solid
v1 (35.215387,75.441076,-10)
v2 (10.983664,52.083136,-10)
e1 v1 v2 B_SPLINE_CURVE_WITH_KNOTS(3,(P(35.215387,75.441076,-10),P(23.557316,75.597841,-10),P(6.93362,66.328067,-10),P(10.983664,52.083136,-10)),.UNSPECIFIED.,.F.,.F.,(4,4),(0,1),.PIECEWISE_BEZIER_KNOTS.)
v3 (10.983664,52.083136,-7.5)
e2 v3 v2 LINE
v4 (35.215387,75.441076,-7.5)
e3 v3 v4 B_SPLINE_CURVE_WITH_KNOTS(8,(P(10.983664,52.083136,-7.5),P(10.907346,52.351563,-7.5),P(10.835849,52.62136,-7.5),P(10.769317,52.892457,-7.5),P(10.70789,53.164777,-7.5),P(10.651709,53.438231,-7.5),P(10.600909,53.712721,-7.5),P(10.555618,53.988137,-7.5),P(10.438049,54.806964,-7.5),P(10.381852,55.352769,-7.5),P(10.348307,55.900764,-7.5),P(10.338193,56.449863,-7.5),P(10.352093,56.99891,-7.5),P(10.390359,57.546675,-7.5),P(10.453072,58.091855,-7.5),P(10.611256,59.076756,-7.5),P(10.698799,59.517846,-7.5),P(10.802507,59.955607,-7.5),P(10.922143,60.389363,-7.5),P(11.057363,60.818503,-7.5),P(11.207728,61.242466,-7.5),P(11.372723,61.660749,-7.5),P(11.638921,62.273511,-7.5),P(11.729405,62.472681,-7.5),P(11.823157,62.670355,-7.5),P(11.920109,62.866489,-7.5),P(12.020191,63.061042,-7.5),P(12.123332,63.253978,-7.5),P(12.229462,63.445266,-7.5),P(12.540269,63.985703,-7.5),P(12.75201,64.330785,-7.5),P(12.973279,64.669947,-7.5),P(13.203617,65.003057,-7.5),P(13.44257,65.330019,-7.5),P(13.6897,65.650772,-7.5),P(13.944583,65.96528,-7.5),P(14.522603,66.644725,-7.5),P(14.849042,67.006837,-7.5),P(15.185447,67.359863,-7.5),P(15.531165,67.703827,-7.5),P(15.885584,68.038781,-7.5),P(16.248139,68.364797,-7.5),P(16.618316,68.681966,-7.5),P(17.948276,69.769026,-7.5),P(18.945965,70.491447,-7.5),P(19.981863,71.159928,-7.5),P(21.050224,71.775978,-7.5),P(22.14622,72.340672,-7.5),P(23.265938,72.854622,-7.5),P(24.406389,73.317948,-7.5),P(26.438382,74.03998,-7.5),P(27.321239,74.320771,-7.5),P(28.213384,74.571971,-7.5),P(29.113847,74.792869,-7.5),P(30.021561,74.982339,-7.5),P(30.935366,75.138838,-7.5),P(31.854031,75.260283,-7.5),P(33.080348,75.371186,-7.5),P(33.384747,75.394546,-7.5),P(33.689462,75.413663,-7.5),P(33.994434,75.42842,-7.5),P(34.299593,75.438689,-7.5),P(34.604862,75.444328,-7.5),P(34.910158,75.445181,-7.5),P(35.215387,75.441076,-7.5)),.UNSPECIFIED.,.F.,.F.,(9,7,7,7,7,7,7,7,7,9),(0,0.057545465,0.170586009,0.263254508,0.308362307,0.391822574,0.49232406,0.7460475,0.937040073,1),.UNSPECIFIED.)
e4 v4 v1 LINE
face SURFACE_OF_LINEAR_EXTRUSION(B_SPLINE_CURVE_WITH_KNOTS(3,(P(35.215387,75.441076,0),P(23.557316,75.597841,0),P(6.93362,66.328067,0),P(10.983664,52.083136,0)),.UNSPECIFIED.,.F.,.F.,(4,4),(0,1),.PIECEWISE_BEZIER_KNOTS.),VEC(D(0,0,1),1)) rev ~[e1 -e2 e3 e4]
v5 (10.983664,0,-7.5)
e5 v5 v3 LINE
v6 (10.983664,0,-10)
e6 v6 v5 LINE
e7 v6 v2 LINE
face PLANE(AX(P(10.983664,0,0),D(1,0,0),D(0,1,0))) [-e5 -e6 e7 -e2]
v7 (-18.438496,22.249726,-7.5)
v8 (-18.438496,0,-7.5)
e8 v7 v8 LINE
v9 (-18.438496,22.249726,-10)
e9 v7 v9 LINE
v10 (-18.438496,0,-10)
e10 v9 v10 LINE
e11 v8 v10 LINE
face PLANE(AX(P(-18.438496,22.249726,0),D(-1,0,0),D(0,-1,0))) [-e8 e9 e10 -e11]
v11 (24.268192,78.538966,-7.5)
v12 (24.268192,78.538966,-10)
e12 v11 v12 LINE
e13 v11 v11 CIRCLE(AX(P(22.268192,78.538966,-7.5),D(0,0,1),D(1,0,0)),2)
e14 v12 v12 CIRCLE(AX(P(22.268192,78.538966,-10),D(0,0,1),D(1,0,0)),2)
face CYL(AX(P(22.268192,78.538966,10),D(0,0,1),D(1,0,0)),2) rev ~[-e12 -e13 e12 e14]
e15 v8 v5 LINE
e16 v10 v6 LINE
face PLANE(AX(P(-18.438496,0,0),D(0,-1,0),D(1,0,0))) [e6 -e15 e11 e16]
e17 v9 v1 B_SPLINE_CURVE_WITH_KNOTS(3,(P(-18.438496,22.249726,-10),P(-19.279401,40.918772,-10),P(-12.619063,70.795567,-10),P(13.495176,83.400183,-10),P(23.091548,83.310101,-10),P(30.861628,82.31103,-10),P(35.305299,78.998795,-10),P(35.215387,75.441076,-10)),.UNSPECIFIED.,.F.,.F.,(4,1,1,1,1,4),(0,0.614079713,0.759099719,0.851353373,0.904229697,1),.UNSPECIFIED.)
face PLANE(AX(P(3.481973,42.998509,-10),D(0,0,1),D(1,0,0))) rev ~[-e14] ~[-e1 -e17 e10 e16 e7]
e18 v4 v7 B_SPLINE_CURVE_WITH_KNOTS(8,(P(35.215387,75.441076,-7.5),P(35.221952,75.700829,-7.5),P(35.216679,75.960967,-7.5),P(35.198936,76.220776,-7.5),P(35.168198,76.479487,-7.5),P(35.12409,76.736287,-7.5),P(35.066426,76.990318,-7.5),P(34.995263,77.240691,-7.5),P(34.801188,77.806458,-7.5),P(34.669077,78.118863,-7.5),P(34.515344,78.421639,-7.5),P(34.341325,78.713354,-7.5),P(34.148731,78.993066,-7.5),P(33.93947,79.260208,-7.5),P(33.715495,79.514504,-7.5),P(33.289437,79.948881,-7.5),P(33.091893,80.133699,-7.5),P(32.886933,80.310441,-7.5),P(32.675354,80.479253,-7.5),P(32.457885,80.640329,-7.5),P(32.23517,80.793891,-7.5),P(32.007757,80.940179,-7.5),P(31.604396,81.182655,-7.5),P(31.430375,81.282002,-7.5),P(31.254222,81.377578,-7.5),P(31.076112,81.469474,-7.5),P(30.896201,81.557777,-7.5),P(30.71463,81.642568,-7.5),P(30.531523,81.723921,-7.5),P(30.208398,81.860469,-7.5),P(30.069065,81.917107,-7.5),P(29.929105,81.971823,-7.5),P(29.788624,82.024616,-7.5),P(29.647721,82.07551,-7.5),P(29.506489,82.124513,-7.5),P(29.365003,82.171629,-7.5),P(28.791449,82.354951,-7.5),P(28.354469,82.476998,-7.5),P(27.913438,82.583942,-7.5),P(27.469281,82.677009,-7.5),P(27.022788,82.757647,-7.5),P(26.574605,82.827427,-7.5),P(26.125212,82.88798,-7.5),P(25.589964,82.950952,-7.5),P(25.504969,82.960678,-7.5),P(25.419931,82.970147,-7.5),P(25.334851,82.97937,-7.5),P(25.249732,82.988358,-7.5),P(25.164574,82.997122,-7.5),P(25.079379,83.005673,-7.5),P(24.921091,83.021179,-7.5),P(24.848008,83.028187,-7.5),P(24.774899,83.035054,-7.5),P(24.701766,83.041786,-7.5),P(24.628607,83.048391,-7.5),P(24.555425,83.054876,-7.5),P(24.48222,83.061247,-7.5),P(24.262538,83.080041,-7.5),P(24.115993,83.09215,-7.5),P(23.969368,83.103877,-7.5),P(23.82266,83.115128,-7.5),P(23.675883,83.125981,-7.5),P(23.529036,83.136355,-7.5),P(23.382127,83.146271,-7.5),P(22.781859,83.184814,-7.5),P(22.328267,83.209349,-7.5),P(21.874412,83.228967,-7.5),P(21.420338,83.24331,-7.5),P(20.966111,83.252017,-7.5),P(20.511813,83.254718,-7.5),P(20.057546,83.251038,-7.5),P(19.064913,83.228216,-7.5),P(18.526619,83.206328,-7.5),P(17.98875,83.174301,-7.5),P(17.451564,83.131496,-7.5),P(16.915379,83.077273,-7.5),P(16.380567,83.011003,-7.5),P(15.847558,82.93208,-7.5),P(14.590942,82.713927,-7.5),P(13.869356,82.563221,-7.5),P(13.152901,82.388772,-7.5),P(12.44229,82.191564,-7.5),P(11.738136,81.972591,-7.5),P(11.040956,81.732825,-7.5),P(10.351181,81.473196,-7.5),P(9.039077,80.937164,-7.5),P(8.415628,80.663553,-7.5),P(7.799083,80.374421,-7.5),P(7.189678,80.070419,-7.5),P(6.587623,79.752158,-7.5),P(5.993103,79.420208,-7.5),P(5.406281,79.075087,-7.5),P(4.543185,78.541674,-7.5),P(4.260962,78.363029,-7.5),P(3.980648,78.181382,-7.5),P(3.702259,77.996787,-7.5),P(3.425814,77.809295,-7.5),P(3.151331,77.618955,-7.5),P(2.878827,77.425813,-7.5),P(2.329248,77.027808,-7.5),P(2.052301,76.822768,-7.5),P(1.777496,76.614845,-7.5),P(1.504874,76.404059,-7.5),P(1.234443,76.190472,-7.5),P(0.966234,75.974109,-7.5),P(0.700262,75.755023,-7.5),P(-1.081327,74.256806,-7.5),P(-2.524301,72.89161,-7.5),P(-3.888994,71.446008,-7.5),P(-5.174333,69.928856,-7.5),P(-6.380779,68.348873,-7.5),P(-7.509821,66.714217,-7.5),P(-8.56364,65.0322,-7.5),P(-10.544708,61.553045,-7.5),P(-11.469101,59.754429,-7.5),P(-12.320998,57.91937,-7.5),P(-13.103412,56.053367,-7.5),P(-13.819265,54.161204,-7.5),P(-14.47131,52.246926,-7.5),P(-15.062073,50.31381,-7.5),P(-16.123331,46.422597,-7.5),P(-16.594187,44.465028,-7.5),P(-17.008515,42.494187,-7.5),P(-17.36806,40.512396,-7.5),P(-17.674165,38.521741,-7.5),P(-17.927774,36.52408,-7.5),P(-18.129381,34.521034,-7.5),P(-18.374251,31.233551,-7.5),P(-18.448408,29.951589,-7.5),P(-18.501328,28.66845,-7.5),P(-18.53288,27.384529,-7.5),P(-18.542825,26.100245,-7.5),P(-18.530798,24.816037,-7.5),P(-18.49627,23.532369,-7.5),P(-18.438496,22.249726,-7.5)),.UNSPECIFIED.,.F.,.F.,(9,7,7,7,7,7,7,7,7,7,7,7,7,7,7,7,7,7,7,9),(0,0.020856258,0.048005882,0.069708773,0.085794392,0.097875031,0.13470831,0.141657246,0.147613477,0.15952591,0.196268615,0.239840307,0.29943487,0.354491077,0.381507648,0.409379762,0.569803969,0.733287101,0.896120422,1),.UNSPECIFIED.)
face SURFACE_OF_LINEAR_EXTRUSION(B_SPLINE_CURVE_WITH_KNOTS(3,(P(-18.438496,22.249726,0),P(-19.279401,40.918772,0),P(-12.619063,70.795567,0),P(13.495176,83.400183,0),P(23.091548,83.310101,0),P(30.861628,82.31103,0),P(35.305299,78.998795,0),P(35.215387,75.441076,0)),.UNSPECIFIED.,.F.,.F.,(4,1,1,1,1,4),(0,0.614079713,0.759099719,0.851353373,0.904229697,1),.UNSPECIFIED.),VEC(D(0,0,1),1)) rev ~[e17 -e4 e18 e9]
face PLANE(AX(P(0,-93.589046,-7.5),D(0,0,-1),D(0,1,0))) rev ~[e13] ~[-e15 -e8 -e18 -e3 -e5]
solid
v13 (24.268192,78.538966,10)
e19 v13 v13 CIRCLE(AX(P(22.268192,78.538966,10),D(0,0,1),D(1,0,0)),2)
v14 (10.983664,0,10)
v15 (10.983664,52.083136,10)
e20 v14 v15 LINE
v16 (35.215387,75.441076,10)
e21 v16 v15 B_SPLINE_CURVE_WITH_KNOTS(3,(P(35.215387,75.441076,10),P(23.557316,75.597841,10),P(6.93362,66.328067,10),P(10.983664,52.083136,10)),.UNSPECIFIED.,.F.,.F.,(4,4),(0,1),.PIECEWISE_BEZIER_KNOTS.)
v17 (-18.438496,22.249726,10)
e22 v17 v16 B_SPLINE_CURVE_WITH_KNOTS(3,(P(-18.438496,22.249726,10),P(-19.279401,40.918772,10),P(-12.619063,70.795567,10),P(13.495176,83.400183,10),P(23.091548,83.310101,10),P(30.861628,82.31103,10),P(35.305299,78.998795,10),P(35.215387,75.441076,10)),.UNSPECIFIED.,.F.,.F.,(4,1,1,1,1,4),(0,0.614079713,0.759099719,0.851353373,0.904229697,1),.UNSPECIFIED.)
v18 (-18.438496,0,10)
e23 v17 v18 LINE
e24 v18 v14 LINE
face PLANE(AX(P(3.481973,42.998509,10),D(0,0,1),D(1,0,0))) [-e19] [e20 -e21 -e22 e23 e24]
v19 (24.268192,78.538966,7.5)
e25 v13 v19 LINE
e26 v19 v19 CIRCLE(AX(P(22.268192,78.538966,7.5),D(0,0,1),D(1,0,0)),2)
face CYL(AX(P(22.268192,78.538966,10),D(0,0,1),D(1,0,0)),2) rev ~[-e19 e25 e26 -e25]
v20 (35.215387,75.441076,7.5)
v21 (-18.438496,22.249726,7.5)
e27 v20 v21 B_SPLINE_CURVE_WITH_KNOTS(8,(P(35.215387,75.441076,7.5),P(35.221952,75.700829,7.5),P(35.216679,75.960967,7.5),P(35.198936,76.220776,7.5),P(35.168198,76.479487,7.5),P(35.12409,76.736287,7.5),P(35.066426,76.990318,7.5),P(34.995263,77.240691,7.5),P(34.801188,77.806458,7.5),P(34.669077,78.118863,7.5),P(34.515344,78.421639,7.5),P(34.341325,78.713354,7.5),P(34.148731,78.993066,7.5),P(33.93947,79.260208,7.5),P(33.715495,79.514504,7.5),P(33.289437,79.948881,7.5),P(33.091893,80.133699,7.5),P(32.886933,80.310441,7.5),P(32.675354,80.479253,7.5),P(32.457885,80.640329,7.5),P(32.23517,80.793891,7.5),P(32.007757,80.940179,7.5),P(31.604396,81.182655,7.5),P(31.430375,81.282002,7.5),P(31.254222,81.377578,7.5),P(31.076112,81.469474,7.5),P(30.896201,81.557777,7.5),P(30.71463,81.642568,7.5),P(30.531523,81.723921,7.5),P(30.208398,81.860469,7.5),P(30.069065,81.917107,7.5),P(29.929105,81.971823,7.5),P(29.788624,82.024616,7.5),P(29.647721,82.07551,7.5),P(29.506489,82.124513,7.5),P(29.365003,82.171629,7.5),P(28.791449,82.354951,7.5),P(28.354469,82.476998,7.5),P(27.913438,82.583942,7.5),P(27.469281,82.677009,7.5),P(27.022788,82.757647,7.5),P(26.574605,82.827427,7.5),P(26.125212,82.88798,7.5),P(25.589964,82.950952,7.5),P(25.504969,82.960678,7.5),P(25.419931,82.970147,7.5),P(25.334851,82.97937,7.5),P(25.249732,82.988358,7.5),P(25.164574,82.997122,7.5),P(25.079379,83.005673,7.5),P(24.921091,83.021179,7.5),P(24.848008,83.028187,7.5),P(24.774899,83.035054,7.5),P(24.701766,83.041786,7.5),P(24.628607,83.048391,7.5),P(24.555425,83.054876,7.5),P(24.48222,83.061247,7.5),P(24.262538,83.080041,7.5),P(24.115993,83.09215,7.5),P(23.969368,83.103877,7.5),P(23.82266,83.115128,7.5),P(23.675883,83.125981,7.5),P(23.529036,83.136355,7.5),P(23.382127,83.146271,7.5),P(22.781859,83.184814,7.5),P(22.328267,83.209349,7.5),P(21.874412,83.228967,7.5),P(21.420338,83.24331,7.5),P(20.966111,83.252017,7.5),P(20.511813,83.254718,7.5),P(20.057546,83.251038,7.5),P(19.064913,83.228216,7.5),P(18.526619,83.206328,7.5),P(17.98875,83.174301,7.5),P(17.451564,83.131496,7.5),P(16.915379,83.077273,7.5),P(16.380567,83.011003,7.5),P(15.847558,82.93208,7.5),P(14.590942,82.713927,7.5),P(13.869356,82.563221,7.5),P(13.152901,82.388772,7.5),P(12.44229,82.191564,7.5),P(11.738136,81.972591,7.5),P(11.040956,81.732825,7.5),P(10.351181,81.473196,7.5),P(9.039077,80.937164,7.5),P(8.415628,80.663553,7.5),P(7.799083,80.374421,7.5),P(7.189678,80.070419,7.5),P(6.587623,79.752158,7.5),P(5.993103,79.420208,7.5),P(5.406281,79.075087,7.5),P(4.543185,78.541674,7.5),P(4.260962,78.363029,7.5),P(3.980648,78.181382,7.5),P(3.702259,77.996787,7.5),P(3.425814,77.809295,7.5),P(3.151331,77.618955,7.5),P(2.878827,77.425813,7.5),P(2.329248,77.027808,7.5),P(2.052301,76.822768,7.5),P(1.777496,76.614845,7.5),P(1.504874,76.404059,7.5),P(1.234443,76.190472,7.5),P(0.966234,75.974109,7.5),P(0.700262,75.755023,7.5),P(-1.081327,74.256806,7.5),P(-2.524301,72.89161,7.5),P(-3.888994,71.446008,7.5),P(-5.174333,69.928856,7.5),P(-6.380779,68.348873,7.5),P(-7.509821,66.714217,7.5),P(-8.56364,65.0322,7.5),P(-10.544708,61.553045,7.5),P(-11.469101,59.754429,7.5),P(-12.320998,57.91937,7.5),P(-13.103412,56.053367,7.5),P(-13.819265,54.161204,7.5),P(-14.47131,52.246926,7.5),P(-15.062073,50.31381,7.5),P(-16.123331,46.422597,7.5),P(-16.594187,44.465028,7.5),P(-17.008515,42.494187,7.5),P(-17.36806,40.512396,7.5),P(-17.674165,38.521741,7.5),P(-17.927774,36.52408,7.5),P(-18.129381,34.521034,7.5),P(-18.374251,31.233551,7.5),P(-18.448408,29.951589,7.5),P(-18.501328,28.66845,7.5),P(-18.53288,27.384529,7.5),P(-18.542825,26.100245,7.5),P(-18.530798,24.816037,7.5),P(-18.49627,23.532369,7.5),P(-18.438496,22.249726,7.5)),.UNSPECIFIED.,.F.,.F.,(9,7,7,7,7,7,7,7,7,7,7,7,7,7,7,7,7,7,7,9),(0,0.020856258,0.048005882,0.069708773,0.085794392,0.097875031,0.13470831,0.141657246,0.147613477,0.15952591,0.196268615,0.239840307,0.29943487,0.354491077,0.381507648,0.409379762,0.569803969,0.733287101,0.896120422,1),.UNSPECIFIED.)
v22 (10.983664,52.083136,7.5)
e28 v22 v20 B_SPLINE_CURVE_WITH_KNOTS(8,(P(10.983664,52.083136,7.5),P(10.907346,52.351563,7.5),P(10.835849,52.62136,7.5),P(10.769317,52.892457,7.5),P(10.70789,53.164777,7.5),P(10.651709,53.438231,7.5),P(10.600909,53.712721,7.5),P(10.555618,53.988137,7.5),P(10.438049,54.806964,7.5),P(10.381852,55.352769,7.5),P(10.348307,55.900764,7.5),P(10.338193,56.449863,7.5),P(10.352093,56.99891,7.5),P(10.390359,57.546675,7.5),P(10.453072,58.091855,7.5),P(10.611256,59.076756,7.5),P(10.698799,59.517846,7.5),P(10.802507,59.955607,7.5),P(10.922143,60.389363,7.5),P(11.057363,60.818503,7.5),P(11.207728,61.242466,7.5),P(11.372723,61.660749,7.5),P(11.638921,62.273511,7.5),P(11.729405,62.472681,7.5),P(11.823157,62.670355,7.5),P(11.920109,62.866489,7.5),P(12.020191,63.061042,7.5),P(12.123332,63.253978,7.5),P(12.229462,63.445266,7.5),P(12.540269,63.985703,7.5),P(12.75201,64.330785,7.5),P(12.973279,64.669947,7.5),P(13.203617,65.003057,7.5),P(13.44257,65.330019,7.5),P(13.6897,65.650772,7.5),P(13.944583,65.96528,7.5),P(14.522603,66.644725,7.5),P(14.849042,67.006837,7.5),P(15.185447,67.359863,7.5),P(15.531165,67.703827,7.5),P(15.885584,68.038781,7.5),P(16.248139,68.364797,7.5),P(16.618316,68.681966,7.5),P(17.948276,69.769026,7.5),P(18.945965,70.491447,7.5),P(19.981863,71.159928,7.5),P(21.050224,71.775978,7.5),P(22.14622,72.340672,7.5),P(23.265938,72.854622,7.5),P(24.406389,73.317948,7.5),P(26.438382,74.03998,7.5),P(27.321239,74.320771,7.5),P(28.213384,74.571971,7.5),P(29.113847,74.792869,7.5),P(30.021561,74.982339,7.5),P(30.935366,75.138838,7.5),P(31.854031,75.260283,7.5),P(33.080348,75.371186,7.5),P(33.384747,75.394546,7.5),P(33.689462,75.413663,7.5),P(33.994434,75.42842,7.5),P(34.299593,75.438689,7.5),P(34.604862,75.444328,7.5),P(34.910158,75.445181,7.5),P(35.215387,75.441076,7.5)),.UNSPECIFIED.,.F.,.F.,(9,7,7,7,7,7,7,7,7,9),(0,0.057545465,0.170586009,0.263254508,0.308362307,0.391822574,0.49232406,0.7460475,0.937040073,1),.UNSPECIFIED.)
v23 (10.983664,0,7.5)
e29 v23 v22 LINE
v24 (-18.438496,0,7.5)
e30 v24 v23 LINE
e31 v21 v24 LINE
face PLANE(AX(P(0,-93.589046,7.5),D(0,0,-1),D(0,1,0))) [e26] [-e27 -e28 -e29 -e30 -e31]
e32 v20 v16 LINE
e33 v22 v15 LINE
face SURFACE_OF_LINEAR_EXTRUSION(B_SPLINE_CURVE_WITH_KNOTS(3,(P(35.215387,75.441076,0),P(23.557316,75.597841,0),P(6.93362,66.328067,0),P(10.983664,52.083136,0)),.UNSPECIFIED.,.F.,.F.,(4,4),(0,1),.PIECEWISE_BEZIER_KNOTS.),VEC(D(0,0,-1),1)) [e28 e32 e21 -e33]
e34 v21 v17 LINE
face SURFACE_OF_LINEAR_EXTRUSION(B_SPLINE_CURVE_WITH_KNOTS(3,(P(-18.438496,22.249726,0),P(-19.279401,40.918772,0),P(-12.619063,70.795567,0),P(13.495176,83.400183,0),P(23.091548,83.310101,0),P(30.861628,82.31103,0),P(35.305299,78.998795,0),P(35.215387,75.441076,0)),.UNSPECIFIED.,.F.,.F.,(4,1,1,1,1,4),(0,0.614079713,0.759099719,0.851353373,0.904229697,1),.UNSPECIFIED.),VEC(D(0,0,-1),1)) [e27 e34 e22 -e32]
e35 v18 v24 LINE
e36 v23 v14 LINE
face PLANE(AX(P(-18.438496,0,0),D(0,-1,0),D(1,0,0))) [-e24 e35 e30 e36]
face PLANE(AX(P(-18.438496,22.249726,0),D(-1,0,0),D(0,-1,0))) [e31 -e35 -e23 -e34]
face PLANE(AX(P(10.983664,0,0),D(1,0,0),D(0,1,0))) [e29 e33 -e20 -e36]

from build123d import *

# Parameters (mm, degrees)
EXTRUDE_1_DEPTH     = 10
SKETCH_5_W          = 15
SKETCH_5_H          = 187.17809157
CUT_EXTRUDE_1_DEPTH = 50
SKETCH_6_R          = 2
CUT_EXTRUDE_2_DEPTH = 100


with BuildPart() as part:
    # 草图4 → 凸台-拉伸1 (new, symmetric)
    with BuildSketch(Plane.XY):
        with BuildLine():
            Line((-18.438496173, 0), (10.983664043, 0))
            Line((10.983664043, 0), (10.983664043, 52.083135501))
            add(Edge.make_bspline(
                [(35.215387482, 75.44107623), (23.557315805, 75.597841168), (6.9336204, 66.328066585), (10.983664043, 52.083135501)],
                knots=[0, 0, 0, 0, 1, 1, 1, 1], degree=3))
            add(Edge.make_bspline(
                [(-18.438496173, 22.249726055), (-19.279401333, 40.918771727), (-12.619063088, 70.795566969), (13.495175546, 83.400182629), (23.091548172, 83.310100579), (30.861628431, 82.311029778), (35.305298589, 78.998794564), (35.215387482, 75.44107623)],
                knots=[0, 0, 0, 0, 0.614079713, 0.759099719, 0.851353373, 0.904229697, 1, 1, 1, 1], degree=3))
            Line((-18.438496173, 22.249726055), (-18.438496173, 0))
        make_face()
    extrude(amount=EXTRUDE_1_DEPTH, both=True)

    # 草图5 → 切除-拉伸1 (cut, symmetric)
    with BuildSketch(Plane(origin=(0, 0, 0), x_dir=(0, 0, -1), z_dir=(1, 0, 0))):
        Rectangle(SKETCH_5_W, SKETCH_5_H)
    extrude(amount=CUT_EXTRUDE_1_DEPTH, both=True, mode=Mode.SUBTRACT)


with BuildPart() as cut_extrude_1_piece_1:
    # of the separate pieces the step leaves, piece 1, a body of its own (cut_extrude_1_pieces)
    add(part.part.solids().sort_by_distance((-18.438496173, 0, -7.5))[0])


with BuildPart() as cut_extrude_1_piece_2:
    # of the separate pieces the step leaves, piece 2, a body of its own (cut_extrude_1_pieces)
    add(part.part.solids().sort_by_distance((-18.438496173, 0, 10))[0])


with BuildPart() as cut_extrude_2_tool:
    # 草图6 → 切除-拉伸2 (new body)
    with BuildSketch(Plane.XY.offset(10)):
        with Locations((22.268192339, 78.538966078)):
            Circle(SKETCH_6_R)
    extrude(amount=-CUT_EXTRUDE_2_DEPTH)


with BuildPart() as cut_extrude_1_piece_1_1:
    add(cut_extrude_1_piece_1.part)

    # 切除-拉伸2: cut by cut_extrude_2_tool
    add(cut_extrude_2_tool.part, mode=Mode.SUBTRACT)


with BuildPart() as cut_extrude_1_piece_2_1:
    add(cut_extrude_1_piece_2.part)

    # 切除-拉伸2: cut by cut_extrude_2_tool
    add(cut_extrude_2_tool.part, mode=Mode.SUBTRACT)


solid = Compound([cut_extrude_1_piece_1_1.part, cut_extrude_1_piece_2_1.part])
